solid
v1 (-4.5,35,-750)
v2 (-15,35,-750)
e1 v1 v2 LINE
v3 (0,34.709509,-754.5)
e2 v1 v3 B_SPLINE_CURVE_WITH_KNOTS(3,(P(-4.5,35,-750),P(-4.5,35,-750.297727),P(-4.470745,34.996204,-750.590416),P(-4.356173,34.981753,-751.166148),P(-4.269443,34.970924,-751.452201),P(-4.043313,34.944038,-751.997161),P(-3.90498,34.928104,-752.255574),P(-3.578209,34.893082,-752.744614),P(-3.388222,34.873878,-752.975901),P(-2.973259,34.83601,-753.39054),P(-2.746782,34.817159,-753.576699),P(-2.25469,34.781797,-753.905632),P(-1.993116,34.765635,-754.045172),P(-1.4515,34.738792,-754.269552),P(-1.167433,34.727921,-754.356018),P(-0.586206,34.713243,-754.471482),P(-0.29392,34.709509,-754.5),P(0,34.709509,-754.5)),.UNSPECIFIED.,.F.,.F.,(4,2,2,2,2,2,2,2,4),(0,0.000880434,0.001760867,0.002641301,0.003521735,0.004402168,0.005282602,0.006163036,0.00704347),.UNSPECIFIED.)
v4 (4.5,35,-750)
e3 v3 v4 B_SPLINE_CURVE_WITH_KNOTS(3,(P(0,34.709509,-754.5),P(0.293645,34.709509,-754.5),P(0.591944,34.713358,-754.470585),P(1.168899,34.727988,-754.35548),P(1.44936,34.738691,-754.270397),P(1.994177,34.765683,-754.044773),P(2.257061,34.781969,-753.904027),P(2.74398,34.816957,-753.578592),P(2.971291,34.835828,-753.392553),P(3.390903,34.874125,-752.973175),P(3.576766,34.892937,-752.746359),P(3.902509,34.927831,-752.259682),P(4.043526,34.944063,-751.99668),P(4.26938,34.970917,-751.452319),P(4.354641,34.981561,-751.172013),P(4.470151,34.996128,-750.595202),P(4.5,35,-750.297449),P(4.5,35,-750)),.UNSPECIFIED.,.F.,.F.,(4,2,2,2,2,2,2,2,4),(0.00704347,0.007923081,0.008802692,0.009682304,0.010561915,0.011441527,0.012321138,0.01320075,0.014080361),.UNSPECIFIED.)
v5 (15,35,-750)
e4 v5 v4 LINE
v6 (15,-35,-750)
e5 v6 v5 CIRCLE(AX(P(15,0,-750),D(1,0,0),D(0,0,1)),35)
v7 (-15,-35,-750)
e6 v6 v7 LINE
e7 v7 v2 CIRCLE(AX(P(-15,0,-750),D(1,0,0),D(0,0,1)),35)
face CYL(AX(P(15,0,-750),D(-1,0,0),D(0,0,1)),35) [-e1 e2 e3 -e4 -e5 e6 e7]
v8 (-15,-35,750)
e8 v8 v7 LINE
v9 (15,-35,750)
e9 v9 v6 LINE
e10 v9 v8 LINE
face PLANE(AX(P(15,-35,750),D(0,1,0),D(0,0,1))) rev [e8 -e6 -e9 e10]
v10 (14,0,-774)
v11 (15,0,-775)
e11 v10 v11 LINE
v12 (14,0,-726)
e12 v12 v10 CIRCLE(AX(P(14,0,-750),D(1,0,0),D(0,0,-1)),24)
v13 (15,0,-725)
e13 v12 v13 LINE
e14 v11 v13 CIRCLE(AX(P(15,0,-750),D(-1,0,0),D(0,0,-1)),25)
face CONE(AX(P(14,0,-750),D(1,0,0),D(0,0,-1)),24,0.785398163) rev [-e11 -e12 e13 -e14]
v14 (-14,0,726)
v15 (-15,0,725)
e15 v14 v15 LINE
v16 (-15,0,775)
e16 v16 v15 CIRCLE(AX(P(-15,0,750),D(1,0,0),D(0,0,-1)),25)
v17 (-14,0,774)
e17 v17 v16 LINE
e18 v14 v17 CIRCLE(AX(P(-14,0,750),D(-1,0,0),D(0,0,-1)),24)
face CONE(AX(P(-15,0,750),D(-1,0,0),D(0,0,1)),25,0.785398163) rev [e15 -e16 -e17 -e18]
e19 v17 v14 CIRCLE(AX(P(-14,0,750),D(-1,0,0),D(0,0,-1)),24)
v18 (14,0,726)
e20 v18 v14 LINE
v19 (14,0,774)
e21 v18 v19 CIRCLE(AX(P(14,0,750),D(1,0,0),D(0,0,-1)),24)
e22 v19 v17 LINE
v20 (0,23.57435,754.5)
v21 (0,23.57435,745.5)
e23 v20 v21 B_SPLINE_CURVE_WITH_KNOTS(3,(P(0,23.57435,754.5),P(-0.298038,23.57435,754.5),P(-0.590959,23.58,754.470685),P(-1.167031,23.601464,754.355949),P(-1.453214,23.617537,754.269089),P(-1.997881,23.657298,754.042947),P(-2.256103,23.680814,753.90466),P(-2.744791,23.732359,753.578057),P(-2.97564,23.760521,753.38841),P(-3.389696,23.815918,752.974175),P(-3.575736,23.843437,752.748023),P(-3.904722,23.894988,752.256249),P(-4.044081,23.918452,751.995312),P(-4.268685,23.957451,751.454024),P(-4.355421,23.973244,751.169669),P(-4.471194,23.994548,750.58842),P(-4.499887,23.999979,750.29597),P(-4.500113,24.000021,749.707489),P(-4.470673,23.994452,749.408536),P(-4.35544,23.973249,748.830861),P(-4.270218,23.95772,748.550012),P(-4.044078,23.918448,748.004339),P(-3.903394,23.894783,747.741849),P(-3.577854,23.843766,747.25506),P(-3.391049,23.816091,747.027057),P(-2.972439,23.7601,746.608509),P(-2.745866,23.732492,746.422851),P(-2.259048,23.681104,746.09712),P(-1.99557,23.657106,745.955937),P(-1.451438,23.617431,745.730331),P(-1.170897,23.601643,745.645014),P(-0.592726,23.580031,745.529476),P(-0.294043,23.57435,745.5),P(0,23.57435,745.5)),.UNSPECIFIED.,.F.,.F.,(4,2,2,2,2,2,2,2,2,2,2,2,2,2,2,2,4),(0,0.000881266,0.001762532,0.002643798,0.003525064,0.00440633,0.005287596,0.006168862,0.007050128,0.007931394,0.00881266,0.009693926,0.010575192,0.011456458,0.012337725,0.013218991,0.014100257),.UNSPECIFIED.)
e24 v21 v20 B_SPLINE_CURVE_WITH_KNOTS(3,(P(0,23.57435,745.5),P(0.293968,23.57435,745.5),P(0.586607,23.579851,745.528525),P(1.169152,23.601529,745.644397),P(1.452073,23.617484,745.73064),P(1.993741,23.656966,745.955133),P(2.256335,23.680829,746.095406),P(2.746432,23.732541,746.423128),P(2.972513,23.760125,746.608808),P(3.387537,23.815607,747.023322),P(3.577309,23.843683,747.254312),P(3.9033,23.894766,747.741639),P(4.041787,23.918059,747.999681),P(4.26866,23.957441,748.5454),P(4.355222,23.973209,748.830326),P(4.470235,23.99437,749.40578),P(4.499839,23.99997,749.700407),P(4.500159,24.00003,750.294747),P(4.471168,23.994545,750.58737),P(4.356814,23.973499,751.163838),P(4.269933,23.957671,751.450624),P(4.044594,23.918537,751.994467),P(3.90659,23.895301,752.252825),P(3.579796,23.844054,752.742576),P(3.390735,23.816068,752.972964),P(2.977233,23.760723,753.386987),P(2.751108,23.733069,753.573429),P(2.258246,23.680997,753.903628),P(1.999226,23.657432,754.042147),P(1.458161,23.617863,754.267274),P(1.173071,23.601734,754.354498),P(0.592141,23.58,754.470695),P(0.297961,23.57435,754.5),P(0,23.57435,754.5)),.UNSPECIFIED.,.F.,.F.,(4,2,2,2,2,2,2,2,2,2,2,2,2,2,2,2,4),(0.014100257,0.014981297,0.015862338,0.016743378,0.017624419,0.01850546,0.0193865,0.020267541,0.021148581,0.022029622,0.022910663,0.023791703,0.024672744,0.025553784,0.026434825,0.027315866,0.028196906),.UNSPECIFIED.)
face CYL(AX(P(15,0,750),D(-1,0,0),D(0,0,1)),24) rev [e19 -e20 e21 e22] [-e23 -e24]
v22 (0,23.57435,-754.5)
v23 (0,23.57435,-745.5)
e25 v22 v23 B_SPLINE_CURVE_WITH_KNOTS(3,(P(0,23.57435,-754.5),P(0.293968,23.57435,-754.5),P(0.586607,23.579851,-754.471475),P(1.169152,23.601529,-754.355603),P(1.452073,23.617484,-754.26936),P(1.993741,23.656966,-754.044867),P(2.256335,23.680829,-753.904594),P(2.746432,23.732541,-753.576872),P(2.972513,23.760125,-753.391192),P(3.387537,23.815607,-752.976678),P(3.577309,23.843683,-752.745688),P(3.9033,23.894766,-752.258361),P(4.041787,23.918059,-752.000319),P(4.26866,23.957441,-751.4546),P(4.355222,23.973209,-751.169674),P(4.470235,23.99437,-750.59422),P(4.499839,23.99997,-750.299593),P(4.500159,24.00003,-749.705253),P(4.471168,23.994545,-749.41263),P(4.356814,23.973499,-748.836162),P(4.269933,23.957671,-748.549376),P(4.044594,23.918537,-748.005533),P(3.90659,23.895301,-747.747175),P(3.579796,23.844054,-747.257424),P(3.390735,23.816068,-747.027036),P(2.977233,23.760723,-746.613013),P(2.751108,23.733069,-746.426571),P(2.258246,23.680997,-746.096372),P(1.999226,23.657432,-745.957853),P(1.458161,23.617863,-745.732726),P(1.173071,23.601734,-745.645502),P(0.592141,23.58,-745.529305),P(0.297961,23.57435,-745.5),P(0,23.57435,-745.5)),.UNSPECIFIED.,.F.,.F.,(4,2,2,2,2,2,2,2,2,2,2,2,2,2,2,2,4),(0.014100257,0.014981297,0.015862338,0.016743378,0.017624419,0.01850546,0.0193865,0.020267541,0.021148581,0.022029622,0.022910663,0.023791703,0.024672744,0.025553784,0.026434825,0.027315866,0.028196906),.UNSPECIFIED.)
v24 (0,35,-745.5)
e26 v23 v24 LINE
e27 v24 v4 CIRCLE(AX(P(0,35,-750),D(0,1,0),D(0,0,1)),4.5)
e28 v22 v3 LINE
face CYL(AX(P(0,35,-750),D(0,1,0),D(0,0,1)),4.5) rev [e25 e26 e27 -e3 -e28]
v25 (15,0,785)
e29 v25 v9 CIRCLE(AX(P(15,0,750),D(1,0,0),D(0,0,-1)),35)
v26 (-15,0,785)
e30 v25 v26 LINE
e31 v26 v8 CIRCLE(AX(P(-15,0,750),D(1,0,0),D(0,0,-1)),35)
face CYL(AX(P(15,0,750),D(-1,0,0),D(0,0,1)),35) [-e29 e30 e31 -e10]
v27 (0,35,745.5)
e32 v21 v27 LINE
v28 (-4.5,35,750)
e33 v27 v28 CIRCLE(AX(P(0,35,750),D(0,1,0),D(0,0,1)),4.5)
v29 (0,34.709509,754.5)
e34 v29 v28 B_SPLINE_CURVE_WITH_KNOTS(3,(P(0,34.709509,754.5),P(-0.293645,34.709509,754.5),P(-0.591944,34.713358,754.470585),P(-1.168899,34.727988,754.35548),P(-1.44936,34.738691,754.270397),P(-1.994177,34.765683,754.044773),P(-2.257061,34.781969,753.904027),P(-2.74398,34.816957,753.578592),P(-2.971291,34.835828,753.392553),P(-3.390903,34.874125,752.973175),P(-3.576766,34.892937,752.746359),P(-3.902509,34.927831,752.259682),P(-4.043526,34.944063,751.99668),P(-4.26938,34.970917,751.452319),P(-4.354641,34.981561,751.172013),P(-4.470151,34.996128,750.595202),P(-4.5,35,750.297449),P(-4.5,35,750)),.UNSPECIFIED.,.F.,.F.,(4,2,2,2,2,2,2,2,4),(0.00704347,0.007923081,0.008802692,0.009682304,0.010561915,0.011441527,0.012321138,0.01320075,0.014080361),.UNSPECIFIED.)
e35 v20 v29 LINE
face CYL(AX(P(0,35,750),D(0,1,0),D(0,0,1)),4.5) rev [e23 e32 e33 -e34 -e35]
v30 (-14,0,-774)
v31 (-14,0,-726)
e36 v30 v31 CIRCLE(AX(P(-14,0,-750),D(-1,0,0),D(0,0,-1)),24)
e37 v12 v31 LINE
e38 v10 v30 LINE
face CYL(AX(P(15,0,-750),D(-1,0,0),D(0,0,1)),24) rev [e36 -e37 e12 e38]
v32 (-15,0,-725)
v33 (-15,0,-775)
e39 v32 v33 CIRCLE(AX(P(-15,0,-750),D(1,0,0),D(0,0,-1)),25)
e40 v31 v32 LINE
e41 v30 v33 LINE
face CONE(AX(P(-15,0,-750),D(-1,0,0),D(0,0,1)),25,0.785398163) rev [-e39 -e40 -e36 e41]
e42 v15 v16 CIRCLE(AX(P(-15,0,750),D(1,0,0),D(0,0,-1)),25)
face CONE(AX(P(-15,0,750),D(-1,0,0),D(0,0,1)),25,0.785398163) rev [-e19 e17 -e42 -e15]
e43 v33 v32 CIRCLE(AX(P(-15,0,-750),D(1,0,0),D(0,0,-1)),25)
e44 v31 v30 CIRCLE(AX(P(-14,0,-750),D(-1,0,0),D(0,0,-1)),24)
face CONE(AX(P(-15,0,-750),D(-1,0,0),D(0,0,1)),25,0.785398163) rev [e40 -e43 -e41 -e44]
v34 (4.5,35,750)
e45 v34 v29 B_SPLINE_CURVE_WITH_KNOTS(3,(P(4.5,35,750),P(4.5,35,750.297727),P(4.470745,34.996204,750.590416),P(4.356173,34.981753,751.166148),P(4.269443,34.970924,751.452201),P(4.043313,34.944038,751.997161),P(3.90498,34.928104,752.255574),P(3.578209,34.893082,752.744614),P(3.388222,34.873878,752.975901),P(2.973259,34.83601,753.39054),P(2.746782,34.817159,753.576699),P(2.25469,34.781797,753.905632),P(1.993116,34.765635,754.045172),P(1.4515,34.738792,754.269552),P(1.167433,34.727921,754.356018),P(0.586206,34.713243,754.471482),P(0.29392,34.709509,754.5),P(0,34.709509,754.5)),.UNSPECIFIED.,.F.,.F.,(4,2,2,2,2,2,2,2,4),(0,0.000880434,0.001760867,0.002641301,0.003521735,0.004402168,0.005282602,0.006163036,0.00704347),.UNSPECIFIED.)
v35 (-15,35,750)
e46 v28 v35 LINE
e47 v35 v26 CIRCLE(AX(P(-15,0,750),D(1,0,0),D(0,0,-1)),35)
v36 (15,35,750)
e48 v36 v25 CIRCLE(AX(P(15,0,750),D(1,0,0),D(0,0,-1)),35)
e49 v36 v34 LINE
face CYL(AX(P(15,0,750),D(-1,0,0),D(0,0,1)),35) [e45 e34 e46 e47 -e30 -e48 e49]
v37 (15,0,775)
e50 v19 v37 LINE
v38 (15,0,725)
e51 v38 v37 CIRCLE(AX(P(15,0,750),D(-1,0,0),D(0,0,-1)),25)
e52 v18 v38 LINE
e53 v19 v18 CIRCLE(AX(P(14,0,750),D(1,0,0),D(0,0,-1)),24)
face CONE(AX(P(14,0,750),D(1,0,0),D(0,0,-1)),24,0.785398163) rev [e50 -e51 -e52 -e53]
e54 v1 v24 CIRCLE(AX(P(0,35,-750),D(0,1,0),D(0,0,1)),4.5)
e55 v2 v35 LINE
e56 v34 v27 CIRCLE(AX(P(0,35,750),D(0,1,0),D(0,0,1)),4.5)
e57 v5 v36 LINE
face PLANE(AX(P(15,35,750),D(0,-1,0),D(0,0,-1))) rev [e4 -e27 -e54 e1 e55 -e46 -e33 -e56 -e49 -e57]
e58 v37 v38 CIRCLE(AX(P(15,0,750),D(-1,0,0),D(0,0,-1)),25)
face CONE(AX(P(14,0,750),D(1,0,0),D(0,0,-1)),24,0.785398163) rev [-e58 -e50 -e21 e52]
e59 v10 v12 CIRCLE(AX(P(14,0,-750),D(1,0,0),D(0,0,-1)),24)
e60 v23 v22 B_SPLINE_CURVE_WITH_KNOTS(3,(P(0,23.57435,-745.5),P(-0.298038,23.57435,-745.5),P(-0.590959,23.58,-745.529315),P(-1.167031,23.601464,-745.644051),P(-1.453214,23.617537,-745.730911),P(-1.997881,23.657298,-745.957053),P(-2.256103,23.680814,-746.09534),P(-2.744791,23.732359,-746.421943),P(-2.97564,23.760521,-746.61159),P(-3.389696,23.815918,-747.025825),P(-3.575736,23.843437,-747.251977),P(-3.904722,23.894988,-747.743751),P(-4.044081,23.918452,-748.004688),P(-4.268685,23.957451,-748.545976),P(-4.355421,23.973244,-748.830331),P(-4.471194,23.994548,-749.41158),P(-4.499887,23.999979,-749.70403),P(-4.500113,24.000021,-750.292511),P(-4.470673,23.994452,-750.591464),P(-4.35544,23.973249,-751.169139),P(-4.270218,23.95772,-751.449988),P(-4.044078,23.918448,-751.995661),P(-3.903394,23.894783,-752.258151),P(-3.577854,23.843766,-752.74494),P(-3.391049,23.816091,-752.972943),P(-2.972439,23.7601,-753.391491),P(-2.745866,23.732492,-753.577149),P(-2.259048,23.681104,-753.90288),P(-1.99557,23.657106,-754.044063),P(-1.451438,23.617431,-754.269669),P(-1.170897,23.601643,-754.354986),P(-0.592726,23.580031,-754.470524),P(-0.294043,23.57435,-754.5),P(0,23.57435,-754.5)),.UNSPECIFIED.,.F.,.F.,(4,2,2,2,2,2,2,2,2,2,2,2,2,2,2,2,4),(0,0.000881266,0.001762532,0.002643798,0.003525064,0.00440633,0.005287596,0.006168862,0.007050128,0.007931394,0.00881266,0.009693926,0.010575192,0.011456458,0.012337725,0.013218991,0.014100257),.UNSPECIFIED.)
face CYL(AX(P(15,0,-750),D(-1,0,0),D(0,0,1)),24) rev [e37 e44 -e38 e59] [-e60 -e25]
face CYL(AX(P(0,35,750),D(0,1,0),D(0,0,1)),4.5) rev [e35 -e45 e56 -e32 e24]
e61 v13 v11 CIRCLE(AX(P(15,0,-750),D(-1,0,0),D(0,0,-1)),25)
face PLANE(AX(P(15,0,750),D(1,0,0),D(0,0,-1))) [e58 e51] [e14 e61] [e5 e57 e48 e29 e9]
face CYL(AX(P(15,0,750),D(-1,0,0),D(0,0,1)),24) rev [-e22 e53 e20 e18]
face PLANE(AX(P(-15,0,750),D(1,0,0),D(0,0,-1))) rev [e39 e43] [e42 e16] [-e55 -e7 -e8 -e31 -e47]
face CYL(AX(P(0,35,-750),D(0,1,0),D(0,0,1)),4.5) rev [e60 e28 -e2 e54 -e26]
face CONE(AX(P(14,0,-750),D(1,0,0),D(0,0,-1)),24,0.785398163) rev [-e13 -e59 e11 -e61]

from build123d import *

# Parameters (mm, degrees)
SKETCH_1_R      = 24
EXTRUDE_1_DEPTH = 15
M10X1_0_1_D     = 9
M10X1_0_1_DEPTH = 20
M10X1_0_1_TIP   = 2.703872786
CHAMFER_1_SIZE  = 1


with BuildPart() as part:
    # 草图1 → 凸台-拉伸1 (new, symmetric)
    with BuildSketch(Plane(origin=(0, 0, 0), x_dir=(0, 0, -1), z_dir=(1, 0, 0))):
        with BuildLine():
            Line((-750, -35), (750, -35))
            ThreePointArc((750, -35), (785, 0), (750, 35))
            Line((750, 35), (-750, 35))
            ThreePointArc((-750, 35), (-785, 0), (-750, -35))
        make_face()
        with Locations((-750, 0)):
            Circle(SKETCH_1_R, mode=Mode.SUBTRACT)
        with Locations((750, 0)):
            Circle(SKETCH_1_R, mode=Mode.SUBTRACT)
    extrude(amount=EXTRUDE_1_DEPTH, both=True)

    # M10x1.0 螺纹孔1
    with Locations(Plane(origin=(0, 35, 0), x_dir=(1, 0, 0), z_dir=(0, 1, 0))):
        with Locations((0, -750), (0, 750)):
            Hole(M10X1_0_1_D / 2, depth=M10X1_0_1_DEPTH)
            with Locations((0, 0, -(M10X1_0_1_DEPTH + M10X1_0_1_TIP / 2))):  # 118° drill point
                Cone(0, M10X1_0_1_D / 2, M10X1_0_1_TIP, mode=Mode.SUBTRACT)

    # 倒角1
    chamfer_1_edges = [part.edges().sort_by_distance(p)[0] for p in [
        (-15, 0, 774),
        (15, 0, 774),
        (-15, 0, -726),
        (15, 0, -726),
    ]]
    chamfer(chamfer_1_edges, length=CHAMFER_1_SIZE)


solid = part.part
